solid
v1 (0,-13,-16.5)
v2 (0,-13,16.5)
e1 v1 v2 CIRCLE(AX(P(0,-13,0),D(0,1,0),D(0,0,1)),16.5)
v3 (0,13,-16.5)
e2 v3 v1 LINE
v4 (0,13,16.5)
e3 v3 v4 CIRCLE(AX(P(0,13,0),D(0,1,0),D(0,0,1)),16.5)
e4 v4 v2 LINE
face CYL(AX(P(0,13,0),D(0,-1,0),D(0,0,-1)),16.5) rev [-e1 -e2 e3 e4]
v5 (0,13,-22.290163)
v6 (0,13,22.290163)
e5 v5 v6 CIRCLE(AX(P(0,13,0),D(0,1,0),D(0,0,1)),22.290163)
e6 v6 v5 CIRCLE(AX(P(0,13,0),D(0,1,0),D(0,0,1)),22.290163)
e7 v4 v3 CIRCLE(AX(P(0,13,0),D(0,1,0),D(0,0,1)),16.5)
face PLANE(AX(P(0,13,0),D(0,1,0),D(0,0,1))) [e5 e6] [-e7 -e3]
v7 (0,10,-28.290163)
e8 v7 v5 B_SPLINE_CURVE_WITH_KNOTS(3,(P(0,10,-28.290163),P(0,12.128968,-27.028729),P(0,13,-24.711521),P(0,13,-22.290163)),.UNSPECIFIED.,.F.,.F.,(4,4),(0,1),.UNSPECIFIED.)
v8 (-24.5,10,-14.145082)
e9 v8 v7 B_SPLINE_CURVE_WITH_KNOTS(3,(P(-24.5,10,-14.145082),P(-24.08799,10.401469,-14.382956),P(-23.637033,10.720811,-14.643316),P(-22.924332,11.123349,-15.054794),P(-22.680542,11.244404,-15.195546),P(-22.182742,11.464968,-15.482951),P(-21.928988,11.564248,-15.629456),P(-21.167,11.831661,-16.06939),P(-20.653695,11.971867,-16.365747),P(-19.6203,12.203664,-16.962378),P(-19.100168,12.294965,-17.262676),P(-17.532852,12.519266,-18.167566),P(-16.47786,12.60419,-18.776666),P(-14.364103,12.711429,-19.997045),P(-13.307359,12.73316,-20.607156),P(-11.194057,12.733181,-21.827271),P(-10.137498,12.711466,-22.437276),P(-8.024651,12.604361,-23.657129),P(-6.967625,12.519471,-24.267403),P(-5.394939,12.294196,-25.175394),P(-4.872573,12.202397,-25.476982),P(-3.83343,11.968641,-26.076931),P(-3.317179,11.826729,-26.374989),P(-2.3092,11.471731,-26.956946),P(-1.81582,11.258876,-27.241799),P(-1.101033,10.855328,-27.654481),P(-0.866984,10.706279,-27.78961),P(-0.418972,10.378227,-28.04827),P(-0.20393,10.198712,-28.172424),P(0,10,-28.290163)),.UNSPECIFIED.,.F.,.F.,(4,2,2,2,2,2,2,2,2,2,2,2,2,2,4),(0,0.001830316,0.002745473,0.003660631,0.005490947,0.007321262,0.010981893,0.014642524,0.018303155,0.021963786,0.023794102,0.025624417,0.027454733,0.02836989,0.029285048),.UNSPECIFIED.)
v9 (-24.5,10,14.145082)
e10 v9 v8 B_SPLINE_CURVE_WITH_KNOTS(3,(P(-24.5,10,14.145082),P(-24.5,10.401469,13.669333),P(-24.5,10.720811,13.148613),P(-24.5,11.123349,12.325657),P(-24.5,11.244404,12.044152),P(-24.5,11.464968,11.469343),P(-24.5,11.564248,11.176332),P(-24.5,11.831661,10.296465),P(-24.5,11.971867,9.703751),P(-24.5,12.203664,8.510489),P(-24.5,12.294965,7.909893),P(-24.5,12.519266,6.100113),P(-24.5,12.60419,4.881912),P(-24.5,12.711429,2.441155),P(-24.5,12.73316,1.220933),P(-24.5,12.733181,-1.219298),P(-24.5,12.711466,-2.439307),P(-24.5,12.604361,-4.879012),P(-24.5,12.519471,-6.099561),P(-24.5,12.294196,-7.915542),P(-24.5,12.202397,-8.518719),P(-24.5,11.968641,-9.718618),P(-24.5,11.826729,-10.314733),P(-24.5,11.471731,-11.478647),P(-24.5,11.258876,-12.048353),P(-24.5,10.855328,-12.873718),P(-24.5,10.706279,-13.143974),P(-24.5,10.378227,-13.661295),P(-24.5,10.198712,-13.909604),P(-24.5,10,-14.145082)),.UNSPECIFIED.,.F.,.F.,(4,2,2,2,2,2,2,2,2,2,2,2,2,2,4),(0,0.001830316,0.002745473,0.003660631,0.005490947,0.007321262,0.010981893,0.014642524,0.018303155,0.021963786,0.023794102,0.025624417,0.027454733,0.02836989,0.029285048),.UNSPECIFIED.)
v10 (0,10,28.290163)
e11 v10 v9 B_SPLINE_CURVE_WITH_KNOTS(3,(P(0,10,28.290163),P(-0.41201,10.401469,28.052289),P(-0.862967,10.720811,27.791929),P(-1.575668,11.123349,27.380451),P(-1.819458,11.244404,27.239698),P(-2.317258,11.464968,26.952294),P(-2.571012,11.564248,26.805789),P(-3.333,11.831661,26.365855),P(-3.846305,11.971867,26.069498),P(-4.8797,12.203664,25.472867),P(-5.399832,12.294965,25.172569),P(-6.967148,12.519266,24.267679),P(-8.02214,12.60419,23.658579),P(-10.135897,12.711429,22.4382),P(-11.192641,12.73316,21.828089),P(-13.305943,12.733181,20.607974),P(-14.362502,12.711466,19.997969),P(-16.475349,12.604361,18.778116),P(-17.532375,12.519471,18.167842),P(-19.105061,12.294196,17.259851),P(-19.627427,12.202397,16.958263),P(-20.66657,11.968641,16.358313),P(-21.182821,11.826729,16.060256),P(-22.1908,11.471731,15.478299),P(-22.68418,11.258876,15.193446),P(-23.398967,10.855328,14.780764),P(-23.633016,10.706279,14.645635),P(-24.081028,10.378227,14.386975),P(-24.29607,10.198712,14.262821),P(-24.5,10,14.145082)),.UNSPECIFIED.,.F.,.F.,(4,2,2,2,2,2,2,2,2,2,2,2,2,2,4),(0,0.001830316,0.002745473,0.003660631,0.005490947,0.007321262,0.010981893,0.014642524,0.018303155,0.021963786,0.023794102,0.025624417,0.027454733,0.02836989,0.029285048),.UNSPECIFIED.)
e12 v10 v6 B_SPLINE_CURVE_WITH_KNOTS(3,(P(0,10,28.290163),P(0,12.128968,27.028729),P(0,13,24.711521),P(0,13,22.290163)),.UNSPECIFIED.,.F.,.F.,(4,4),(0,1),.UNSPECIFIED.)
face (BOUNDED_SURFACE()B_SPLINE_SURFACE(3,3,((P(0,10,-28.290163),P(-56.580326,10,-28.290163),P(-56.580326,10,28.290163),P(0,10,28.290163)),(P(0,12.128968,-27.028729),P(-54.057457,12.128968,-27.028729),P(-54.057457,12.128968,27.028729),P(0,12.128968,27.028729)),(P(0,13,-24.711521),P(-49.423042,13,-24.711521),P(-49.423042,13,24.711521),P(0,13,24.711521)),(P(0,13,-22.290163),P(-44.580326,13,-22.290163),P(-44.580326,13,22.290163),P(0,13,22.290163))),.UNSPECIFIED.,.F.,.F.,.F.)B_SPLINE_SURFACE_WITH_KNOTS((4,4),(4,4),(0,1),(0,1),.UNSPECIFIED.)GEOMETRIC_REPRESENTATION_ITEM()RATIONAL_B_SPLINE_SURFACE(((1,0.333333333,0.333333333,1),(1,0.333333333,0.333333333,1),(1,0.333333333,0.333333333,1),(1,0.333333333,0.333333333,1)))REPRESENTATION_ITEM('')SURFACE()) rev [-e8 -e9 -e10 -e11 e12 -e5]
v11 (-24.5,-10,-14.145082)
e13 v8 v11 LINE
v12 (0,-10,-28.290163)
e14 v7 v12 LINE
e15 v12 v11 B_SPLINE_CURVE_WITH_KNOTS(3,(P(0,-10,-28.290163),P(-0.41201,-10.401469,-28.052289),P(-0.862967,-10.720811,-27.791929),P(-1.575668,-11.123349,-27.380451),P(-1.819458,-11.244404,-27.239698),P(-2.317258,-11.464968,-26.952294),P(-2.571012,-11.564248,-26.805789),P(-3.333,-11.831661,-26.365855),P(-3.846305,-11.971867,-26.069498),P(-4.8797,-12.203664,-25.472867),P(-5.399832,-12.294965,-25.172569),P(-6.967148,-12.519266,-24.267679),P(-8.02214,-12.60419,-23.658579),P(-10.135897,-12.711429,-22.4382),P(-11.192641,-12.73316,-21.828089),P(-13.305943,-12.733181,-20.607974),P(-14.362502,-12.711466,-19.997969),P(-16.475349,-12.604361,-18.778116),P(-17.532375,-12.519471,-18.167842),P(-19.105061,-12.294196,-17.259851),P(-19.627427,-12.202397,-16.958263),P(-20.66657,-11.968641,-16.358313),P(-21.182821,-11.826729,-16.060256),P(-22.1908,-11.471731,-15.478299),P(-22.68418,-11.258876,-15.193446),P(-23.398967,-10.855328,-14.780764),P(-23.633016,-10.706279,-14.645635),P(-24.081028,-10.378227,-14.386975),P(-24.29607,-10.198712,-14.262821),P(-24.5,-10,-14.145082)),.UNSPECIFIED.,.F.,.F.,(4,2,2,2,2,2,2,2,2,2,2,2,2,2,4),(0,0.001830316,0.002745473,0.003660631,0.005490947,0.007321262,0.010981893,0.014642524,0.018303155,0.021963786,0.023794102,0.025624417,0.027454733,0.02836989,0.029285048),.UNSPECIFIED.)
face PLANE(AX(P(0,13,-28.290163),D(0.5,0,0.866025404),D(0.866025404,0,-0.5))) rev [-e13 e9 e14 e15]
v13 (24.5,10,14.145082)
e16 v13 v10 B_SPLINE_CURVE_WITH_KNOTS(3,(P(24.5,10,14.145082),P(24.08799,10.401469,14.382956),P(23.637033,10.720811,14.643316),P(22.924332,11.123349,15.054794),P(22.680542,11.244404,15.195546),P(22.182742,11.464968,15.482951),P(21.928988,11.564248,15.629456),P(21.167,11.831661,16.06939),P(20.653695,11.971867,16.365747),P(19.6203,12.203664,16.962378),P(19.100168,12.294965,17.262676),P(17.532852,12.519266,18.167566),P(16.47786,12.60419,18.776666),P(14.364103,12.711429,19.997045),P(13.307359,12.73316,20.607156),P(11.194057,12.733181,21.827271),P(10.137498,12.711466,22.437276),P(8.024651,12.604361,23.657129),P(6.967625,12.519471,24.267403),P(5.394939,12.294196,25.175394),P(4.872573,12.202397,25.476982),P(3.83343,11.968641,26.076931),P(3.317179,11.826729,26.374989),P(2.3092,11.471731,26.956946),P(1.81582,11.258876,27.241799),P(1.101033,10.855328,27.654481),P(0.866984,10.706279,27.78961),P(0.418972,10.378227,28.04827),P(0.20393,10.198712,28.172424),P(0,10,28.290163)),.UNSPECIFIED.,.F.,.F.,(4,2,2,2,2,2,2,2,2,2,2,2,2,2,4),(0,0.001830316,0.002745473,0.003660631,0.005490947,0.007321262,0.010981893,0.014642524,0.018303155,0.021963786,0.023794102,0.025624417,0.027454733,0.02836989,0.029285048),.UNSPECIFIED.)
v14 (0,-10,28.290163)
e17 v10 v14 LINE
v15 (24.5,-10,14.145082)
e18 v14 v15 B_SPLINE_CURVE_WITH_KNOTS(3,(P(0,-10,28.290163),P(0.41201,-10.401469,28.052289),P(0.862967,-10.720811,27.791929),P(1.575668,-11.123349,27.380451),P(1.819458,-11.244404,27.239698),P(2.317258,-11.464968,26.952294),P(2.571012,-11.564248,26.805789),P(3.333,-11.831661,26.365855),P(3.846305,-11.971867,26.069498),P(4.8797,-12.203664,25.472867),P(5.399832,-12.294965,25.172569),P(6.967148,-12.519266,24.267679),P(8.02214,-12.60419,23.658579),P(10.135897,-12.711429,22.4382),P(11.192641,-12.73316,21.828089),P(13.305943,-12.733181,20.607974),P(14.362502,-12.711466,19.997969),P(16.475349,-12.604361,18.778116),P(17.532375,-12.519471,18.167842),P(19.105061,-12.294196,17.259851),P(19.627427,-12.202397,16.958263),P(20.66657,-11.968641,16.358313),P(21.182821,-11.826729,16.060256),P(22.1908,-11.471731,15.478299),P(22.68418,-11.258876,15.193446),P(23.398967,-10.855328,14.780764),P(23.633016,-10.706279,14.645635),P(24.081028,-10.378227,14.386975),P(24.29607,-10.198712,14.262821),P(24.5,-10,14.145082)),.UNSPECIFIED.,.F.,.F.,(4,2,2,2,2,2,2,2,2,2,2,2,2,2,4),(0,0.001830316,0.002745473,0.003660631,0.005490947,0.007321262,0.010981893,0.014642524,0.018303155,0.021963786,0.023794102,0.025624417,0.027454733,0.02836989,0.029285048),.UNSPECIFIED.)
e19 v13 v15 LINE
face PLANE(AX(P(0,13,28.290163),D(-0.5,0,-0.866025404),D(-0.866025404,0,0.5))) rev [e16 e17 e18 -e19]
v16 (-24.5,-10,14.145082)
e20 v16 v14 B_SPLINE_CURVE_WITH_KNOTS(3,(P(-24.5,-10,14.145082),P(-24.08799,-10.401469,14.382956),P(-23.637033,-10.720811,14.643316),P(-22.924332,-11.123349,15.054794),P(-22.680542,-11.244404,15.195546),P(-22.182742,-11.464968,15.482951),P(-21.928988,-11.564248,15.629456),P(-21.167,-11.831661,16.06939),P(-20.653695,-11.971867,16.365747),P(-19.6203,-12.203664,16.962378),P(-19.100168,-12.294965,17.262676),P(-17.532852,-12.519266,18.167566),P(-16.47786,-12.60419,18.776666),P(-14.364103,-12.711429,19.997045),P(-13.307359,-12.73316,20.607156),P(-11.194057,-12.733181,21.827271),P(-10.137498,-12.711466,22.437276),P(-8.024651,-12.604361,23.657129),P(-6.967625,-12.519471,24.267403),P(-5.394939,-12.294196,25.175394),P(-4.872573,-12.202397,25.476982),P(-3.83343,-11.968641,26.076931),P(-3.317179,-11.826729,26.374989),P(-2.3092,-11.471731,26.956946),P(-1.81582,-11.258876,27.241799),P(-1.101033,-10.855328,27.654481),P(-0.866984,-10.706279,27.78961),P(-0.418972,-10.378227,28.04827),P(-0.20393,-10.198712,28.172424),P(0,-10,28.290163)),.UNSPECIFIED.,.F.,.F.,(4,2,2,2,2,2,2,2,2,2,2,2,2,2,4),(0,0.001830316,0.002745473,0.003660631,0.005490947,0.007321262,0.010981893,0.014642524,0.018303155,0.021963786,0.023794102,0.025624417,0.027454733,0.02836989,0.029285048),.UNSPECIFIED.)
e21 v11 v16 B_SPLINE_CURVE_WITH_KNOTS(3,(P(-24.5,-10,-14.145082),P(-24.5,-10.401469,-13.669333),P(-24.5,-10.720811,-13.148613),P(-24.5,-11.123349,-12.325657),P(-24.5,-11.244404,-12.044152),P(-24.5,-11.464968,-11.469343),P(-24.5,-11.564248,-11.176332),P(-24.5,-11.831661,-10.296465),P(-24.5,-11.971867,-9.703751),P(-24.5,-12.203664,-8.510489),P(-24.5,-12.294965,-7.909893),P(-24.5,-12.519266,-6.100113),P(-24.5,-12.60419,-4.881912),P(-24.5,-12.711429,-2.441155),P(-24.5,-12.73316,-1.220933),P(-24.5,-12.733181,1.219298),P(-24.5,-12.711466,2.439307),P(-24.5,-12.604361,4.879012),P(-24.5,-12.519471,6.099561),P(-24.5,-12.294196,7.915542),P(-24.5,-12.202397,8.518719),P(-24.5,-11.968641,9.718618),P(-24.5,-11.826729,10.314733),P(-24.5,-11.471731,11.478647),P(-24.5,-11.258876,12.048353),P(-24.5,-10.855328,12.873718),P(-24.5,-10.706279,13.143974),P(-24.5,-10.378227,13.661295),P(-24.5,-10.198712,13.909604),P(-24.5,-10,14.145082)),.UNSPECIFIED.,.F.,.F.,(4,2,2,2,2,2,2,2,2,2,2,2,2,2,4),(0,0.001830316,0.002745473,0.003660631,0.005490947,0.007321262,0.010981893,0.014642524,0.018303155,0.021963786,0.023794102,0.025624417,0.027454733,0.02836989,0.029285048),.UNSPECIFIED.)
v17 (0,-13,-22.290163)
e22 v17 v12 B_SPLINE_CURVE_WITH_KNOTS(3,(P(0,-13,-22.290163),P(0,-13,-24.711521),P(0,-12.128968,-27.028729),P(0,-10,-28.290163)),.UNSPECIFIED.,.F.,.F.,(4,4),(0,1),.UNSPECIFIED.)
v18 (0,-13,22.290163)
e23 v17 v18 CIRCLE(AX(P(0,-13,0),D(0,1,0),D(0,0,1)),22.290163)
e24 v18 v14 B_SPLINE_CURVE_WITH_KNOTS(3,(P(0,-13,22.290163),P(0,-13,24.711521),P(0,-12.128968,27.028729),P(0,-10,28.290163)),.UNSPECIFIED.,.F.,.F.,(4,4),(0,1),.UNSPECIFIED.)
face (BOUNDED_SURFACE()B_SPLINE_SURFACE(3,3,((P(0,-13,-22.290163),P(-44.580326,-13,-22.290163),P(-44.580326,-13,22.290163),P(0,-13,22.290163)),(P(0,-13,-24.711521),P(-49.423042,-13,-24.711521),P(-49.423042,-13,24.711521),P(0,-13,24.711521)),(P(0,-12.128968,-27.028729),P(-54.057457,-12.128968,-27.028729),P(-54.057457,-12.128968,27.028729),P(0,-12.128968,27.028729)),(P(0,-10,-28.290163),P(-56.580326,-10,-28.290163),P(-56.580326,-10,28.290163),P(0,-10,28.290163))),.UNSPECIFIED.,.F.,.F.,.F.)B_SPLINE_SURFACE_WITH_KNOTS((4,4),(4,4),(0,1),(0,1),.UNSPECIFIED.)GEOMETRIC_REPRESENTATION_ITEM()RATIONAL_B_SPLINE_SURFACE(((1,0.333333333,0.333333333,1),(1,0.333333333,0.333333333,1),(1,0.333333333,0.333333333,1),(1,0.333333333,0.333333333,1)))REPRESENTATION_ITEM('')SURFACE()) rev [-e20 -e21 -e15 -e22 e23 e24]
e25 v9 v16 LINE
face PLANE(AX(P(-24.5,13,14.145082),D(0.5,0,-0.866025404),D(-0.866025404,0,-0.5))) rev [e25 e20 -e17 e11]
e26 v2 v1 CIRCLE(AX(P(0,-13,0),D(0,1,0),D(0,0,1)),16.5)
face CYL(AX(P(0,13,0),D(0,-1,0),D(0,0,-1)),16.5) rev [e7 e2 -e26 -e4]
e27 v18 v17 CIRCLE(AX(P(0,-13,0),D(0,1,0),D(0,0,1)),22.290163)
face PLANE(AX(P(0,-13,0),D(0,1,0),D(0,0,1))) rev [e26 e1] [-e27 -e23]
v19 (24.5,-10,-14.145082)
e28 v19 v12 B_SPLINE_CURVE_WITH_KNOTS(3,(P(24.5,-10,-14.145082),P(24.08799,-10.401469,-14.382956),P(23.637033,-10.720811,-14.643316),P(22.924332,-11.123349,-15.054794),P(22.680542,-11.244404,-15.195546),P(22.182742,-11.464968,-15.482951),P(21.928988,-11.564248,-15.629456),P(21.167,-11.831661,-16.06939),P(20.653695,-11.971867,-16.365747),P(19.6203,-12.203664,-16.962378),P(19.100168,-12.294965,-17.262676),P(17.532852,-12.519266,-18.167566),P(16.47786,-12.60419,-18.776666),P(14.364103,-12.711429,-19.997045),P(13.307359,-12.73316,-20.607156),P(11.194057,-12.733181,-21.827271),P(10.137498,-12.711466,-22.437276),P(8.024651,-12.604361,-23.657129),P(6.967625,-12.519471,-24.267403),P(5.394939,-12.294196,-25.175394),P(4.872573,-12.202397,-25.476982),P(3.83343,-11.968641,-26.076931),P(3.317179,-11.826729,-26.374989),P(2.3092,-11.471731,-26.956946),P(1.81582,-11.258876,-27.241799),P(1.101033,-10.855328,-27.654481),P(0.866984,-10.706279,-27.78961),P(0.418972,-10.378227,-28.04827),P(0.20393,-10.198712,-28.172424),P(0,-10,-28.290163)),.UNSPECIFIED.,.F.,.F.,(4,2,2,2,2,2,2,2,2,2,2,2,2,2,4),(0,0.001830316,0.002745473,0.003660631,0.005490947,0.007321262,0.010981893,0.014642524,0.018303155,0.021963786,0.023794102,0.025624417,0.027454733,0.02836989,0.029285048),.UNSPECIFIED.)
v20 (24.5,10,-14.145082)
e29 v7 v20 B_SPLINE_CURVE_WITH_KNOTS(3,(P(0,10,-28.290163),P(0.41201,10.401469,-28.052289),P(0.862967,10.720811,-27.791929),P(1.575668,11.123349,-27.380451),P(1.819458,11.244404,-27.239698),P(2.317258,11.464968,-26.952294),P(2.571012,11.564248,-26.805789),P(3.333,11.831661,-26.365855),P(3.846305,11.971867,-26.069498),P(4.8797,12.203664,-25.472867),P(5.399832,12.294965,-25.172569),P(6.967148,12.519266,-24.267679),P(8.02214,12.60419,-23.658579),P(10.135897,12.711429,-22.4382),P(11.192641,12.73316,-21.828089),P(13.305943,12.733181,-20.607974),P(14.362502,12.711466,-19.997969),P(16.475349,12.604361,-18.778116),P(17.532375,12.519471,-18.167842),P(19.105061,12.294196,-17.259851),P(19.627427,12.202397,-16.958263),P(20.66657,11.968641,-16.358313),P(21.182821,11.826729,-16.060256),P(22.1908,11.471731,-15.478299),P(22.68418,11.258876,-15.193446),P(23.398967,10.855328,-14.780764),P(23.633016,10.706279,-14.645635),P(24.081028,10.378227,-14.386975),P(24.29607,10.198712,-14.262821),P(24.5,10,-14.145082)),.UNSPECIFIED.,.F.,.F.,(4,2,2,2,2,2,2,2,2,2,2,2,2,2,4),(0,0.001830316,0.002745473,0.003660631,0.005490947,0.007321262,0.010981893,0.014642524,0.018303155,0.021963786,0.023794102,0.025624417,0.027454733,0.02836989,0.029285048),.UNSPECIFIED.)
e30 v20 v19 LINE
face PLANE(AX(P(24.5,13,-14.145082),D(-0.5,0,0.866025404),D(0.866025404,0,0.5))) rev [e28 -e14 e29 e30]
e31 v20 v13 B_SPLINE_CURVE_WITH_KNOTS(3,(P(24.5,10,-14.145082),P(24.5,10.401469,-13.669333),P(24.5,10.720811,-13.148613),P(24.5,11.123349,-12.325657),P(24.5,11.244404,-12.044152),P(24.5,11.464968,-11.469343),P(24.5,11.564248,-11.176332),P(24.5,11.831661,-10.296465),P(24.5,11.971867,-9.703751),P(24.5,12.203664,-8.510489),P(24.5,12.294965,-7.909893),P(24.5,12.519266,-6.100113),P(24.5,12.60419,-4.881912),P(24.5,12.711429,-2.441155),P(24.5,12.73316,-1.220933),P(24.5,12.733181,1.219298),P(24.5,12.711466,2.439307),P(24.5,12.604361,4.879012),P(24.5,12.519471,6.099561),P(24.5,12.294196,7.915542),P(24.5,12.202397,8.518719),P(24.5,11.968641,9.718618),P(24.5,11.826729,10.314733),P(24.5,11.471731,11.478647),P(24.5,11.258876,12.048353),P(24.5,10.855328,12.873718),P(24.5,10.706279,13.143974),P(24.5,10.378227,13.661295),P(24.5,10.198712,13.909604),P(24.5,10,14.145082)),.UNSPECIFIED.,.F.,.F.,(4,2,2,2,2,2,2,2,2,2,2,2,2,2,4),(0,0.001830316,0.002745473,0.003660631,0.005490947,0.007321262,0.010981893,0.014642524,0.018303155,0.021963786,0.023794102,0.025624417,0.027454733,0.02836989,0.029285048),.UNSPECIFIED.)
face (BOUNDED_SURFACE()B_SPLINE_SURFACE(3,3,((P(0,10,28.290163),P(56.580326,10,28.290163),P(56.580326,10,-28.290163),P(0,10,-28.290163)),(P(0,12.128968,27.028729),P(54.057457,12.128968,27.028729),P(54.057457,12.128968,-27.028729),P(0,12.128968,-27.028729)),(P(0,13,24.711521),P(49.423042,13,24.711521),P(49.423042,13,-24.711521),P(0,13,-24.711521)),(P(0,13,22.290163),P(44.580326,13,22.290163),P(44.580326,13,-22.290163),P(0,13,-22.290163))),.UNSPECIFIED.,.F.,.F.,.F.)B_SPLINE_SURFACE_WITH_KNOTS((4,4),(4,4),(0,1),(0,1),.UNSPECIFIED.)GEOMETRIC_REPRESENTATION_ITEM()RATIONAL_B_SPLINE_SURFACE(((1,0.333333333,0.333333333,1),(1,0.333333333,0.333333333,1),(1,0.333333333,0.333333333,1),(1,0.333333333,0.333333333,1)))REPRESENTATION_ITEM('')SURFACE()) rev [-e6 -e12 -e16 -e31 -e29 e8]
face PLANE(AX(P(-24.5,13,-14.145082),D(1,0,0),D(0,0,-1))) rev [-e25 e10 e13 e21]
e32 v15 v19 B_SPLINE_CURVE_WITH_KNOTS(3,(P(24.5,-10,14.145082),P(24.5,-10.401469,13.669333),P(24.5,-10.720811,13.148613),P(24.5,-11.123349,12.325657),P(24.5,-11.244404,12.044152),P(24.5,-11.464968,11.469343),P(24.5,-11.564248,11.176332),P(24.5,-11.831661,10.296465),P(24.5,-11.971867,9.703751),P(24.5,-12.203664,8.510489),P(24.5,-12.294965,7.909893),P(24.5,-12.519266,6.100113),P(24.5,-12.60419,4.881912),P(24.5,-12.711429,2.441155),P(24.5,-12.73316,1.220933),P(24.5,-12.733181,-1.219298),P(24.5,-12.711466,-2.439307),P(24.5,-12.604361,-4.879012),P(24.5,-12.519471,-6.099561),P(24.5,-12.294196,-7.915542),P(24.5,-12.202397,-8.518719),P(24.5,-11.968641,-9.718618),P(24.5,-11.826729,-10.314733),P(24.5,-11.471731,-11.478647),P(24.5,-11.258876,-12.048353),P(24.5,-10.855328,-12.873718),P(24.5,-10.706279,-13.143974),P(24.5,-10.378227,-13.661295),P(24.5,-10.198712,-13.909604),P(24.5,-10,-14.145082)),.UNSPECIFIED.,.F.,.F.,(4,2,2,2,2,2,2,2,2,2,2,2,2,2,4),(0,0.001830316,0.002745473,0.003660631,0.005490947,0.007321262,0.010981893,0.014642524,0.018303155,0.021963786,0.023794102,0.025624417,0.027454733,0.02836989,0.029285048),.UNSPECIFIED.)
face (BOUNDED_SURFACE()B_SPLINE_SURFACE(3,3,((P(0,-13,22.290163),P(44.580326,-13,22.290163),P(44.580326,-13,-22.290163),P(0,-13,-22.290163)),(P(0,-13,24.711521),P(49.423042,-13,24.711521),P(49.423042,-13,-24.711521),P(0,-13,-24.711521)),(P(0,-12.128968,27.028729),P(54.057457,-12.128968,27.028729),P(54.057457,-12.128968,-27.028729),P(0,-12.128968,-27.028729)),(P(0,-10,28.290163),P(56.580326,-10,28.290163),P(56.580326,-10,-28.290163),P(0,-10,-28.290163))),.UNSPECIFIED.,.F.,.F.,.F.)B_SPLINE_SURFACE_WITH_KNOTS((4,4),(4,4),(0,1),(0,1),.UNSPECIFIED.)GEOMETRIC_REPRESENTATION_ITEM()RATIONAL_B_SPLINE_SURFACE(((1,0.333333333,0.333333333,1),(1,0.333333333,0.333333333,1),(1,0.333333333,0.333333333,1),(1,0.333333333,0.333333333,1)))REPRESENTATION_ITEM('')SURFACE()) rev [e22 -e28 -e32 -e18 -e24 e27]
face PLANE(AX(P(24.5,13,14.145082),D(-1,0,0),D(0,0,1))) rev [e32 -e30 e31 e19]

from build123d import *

# Parameters (mm, degrees)
SKETCH_1_R           = 16.5
BOSS_EXTRUDE_1_DEPTH = 13


with BuildPart() as part:
    # Sketch 1 → Boss-Extrude 1 (new, symmetric)
    with BuildSketch(Plane(origin=(0, 0, 0), x_dir=(1, 0, 0), z_dir=(0, 1, 0))):
        Polygon((0, 28.29016319), (-24.5, 14.145081595), (-24.5, -14.145081595), (0, -28.29016319), (24.5, -14.145081595), (24.5, 14.145081595), align=None)
        with Locations(Location((0, 0, 0), (0, 0, 90))):
            Circle(SKETCH_1_R, mode=Mode.SUBTRACT)
    extrude(amount=BOSS_EXTRUDE_1_DEPTH, both=True)

    # Sketch 2 → Cut-Revolve 1 (revolve, cut)
    with BuildSketch(Plane(origin=(0, 0, 0), x_dir=(0, 0, -1), z_dir=(1, 0, 0))):
        with BuildLine():
            Line((-22.29016319, 13), (-28.29016319, 13))
            Line((-28.29016319, 13), (-28.29016319, 10))
            add(Edge.make_bspline(
                [(-28.29016319, 10), (-27.028728561, 12.12896823), (-24.711520857, 13), (-22.29016319, 13)],
                knots=[0, 0, 0, 0, 1, 1, 1, 1], degree=3))
        make_face()
        with BuildLine():
            Line((-28.29016319, -13), (-28.29016319, -10))
            add(Edge.make_bspline(
                [(-28.29016319, -10), (-27.028728561, -12.12896823), (-24.711520857, -13), (-22.29016319, -13)],
                knots=[0, 0, 0, 0, 1, 1, 1, 1], degree=3))
            Line((-22.29016319, -13), (-28.29016319, -13))
        make_face()
    revolve(axis=Axis((0, 20.720193417, 0), (0, -1, 0)), mode=Mode.SUBTRACT)


solid = part.part
